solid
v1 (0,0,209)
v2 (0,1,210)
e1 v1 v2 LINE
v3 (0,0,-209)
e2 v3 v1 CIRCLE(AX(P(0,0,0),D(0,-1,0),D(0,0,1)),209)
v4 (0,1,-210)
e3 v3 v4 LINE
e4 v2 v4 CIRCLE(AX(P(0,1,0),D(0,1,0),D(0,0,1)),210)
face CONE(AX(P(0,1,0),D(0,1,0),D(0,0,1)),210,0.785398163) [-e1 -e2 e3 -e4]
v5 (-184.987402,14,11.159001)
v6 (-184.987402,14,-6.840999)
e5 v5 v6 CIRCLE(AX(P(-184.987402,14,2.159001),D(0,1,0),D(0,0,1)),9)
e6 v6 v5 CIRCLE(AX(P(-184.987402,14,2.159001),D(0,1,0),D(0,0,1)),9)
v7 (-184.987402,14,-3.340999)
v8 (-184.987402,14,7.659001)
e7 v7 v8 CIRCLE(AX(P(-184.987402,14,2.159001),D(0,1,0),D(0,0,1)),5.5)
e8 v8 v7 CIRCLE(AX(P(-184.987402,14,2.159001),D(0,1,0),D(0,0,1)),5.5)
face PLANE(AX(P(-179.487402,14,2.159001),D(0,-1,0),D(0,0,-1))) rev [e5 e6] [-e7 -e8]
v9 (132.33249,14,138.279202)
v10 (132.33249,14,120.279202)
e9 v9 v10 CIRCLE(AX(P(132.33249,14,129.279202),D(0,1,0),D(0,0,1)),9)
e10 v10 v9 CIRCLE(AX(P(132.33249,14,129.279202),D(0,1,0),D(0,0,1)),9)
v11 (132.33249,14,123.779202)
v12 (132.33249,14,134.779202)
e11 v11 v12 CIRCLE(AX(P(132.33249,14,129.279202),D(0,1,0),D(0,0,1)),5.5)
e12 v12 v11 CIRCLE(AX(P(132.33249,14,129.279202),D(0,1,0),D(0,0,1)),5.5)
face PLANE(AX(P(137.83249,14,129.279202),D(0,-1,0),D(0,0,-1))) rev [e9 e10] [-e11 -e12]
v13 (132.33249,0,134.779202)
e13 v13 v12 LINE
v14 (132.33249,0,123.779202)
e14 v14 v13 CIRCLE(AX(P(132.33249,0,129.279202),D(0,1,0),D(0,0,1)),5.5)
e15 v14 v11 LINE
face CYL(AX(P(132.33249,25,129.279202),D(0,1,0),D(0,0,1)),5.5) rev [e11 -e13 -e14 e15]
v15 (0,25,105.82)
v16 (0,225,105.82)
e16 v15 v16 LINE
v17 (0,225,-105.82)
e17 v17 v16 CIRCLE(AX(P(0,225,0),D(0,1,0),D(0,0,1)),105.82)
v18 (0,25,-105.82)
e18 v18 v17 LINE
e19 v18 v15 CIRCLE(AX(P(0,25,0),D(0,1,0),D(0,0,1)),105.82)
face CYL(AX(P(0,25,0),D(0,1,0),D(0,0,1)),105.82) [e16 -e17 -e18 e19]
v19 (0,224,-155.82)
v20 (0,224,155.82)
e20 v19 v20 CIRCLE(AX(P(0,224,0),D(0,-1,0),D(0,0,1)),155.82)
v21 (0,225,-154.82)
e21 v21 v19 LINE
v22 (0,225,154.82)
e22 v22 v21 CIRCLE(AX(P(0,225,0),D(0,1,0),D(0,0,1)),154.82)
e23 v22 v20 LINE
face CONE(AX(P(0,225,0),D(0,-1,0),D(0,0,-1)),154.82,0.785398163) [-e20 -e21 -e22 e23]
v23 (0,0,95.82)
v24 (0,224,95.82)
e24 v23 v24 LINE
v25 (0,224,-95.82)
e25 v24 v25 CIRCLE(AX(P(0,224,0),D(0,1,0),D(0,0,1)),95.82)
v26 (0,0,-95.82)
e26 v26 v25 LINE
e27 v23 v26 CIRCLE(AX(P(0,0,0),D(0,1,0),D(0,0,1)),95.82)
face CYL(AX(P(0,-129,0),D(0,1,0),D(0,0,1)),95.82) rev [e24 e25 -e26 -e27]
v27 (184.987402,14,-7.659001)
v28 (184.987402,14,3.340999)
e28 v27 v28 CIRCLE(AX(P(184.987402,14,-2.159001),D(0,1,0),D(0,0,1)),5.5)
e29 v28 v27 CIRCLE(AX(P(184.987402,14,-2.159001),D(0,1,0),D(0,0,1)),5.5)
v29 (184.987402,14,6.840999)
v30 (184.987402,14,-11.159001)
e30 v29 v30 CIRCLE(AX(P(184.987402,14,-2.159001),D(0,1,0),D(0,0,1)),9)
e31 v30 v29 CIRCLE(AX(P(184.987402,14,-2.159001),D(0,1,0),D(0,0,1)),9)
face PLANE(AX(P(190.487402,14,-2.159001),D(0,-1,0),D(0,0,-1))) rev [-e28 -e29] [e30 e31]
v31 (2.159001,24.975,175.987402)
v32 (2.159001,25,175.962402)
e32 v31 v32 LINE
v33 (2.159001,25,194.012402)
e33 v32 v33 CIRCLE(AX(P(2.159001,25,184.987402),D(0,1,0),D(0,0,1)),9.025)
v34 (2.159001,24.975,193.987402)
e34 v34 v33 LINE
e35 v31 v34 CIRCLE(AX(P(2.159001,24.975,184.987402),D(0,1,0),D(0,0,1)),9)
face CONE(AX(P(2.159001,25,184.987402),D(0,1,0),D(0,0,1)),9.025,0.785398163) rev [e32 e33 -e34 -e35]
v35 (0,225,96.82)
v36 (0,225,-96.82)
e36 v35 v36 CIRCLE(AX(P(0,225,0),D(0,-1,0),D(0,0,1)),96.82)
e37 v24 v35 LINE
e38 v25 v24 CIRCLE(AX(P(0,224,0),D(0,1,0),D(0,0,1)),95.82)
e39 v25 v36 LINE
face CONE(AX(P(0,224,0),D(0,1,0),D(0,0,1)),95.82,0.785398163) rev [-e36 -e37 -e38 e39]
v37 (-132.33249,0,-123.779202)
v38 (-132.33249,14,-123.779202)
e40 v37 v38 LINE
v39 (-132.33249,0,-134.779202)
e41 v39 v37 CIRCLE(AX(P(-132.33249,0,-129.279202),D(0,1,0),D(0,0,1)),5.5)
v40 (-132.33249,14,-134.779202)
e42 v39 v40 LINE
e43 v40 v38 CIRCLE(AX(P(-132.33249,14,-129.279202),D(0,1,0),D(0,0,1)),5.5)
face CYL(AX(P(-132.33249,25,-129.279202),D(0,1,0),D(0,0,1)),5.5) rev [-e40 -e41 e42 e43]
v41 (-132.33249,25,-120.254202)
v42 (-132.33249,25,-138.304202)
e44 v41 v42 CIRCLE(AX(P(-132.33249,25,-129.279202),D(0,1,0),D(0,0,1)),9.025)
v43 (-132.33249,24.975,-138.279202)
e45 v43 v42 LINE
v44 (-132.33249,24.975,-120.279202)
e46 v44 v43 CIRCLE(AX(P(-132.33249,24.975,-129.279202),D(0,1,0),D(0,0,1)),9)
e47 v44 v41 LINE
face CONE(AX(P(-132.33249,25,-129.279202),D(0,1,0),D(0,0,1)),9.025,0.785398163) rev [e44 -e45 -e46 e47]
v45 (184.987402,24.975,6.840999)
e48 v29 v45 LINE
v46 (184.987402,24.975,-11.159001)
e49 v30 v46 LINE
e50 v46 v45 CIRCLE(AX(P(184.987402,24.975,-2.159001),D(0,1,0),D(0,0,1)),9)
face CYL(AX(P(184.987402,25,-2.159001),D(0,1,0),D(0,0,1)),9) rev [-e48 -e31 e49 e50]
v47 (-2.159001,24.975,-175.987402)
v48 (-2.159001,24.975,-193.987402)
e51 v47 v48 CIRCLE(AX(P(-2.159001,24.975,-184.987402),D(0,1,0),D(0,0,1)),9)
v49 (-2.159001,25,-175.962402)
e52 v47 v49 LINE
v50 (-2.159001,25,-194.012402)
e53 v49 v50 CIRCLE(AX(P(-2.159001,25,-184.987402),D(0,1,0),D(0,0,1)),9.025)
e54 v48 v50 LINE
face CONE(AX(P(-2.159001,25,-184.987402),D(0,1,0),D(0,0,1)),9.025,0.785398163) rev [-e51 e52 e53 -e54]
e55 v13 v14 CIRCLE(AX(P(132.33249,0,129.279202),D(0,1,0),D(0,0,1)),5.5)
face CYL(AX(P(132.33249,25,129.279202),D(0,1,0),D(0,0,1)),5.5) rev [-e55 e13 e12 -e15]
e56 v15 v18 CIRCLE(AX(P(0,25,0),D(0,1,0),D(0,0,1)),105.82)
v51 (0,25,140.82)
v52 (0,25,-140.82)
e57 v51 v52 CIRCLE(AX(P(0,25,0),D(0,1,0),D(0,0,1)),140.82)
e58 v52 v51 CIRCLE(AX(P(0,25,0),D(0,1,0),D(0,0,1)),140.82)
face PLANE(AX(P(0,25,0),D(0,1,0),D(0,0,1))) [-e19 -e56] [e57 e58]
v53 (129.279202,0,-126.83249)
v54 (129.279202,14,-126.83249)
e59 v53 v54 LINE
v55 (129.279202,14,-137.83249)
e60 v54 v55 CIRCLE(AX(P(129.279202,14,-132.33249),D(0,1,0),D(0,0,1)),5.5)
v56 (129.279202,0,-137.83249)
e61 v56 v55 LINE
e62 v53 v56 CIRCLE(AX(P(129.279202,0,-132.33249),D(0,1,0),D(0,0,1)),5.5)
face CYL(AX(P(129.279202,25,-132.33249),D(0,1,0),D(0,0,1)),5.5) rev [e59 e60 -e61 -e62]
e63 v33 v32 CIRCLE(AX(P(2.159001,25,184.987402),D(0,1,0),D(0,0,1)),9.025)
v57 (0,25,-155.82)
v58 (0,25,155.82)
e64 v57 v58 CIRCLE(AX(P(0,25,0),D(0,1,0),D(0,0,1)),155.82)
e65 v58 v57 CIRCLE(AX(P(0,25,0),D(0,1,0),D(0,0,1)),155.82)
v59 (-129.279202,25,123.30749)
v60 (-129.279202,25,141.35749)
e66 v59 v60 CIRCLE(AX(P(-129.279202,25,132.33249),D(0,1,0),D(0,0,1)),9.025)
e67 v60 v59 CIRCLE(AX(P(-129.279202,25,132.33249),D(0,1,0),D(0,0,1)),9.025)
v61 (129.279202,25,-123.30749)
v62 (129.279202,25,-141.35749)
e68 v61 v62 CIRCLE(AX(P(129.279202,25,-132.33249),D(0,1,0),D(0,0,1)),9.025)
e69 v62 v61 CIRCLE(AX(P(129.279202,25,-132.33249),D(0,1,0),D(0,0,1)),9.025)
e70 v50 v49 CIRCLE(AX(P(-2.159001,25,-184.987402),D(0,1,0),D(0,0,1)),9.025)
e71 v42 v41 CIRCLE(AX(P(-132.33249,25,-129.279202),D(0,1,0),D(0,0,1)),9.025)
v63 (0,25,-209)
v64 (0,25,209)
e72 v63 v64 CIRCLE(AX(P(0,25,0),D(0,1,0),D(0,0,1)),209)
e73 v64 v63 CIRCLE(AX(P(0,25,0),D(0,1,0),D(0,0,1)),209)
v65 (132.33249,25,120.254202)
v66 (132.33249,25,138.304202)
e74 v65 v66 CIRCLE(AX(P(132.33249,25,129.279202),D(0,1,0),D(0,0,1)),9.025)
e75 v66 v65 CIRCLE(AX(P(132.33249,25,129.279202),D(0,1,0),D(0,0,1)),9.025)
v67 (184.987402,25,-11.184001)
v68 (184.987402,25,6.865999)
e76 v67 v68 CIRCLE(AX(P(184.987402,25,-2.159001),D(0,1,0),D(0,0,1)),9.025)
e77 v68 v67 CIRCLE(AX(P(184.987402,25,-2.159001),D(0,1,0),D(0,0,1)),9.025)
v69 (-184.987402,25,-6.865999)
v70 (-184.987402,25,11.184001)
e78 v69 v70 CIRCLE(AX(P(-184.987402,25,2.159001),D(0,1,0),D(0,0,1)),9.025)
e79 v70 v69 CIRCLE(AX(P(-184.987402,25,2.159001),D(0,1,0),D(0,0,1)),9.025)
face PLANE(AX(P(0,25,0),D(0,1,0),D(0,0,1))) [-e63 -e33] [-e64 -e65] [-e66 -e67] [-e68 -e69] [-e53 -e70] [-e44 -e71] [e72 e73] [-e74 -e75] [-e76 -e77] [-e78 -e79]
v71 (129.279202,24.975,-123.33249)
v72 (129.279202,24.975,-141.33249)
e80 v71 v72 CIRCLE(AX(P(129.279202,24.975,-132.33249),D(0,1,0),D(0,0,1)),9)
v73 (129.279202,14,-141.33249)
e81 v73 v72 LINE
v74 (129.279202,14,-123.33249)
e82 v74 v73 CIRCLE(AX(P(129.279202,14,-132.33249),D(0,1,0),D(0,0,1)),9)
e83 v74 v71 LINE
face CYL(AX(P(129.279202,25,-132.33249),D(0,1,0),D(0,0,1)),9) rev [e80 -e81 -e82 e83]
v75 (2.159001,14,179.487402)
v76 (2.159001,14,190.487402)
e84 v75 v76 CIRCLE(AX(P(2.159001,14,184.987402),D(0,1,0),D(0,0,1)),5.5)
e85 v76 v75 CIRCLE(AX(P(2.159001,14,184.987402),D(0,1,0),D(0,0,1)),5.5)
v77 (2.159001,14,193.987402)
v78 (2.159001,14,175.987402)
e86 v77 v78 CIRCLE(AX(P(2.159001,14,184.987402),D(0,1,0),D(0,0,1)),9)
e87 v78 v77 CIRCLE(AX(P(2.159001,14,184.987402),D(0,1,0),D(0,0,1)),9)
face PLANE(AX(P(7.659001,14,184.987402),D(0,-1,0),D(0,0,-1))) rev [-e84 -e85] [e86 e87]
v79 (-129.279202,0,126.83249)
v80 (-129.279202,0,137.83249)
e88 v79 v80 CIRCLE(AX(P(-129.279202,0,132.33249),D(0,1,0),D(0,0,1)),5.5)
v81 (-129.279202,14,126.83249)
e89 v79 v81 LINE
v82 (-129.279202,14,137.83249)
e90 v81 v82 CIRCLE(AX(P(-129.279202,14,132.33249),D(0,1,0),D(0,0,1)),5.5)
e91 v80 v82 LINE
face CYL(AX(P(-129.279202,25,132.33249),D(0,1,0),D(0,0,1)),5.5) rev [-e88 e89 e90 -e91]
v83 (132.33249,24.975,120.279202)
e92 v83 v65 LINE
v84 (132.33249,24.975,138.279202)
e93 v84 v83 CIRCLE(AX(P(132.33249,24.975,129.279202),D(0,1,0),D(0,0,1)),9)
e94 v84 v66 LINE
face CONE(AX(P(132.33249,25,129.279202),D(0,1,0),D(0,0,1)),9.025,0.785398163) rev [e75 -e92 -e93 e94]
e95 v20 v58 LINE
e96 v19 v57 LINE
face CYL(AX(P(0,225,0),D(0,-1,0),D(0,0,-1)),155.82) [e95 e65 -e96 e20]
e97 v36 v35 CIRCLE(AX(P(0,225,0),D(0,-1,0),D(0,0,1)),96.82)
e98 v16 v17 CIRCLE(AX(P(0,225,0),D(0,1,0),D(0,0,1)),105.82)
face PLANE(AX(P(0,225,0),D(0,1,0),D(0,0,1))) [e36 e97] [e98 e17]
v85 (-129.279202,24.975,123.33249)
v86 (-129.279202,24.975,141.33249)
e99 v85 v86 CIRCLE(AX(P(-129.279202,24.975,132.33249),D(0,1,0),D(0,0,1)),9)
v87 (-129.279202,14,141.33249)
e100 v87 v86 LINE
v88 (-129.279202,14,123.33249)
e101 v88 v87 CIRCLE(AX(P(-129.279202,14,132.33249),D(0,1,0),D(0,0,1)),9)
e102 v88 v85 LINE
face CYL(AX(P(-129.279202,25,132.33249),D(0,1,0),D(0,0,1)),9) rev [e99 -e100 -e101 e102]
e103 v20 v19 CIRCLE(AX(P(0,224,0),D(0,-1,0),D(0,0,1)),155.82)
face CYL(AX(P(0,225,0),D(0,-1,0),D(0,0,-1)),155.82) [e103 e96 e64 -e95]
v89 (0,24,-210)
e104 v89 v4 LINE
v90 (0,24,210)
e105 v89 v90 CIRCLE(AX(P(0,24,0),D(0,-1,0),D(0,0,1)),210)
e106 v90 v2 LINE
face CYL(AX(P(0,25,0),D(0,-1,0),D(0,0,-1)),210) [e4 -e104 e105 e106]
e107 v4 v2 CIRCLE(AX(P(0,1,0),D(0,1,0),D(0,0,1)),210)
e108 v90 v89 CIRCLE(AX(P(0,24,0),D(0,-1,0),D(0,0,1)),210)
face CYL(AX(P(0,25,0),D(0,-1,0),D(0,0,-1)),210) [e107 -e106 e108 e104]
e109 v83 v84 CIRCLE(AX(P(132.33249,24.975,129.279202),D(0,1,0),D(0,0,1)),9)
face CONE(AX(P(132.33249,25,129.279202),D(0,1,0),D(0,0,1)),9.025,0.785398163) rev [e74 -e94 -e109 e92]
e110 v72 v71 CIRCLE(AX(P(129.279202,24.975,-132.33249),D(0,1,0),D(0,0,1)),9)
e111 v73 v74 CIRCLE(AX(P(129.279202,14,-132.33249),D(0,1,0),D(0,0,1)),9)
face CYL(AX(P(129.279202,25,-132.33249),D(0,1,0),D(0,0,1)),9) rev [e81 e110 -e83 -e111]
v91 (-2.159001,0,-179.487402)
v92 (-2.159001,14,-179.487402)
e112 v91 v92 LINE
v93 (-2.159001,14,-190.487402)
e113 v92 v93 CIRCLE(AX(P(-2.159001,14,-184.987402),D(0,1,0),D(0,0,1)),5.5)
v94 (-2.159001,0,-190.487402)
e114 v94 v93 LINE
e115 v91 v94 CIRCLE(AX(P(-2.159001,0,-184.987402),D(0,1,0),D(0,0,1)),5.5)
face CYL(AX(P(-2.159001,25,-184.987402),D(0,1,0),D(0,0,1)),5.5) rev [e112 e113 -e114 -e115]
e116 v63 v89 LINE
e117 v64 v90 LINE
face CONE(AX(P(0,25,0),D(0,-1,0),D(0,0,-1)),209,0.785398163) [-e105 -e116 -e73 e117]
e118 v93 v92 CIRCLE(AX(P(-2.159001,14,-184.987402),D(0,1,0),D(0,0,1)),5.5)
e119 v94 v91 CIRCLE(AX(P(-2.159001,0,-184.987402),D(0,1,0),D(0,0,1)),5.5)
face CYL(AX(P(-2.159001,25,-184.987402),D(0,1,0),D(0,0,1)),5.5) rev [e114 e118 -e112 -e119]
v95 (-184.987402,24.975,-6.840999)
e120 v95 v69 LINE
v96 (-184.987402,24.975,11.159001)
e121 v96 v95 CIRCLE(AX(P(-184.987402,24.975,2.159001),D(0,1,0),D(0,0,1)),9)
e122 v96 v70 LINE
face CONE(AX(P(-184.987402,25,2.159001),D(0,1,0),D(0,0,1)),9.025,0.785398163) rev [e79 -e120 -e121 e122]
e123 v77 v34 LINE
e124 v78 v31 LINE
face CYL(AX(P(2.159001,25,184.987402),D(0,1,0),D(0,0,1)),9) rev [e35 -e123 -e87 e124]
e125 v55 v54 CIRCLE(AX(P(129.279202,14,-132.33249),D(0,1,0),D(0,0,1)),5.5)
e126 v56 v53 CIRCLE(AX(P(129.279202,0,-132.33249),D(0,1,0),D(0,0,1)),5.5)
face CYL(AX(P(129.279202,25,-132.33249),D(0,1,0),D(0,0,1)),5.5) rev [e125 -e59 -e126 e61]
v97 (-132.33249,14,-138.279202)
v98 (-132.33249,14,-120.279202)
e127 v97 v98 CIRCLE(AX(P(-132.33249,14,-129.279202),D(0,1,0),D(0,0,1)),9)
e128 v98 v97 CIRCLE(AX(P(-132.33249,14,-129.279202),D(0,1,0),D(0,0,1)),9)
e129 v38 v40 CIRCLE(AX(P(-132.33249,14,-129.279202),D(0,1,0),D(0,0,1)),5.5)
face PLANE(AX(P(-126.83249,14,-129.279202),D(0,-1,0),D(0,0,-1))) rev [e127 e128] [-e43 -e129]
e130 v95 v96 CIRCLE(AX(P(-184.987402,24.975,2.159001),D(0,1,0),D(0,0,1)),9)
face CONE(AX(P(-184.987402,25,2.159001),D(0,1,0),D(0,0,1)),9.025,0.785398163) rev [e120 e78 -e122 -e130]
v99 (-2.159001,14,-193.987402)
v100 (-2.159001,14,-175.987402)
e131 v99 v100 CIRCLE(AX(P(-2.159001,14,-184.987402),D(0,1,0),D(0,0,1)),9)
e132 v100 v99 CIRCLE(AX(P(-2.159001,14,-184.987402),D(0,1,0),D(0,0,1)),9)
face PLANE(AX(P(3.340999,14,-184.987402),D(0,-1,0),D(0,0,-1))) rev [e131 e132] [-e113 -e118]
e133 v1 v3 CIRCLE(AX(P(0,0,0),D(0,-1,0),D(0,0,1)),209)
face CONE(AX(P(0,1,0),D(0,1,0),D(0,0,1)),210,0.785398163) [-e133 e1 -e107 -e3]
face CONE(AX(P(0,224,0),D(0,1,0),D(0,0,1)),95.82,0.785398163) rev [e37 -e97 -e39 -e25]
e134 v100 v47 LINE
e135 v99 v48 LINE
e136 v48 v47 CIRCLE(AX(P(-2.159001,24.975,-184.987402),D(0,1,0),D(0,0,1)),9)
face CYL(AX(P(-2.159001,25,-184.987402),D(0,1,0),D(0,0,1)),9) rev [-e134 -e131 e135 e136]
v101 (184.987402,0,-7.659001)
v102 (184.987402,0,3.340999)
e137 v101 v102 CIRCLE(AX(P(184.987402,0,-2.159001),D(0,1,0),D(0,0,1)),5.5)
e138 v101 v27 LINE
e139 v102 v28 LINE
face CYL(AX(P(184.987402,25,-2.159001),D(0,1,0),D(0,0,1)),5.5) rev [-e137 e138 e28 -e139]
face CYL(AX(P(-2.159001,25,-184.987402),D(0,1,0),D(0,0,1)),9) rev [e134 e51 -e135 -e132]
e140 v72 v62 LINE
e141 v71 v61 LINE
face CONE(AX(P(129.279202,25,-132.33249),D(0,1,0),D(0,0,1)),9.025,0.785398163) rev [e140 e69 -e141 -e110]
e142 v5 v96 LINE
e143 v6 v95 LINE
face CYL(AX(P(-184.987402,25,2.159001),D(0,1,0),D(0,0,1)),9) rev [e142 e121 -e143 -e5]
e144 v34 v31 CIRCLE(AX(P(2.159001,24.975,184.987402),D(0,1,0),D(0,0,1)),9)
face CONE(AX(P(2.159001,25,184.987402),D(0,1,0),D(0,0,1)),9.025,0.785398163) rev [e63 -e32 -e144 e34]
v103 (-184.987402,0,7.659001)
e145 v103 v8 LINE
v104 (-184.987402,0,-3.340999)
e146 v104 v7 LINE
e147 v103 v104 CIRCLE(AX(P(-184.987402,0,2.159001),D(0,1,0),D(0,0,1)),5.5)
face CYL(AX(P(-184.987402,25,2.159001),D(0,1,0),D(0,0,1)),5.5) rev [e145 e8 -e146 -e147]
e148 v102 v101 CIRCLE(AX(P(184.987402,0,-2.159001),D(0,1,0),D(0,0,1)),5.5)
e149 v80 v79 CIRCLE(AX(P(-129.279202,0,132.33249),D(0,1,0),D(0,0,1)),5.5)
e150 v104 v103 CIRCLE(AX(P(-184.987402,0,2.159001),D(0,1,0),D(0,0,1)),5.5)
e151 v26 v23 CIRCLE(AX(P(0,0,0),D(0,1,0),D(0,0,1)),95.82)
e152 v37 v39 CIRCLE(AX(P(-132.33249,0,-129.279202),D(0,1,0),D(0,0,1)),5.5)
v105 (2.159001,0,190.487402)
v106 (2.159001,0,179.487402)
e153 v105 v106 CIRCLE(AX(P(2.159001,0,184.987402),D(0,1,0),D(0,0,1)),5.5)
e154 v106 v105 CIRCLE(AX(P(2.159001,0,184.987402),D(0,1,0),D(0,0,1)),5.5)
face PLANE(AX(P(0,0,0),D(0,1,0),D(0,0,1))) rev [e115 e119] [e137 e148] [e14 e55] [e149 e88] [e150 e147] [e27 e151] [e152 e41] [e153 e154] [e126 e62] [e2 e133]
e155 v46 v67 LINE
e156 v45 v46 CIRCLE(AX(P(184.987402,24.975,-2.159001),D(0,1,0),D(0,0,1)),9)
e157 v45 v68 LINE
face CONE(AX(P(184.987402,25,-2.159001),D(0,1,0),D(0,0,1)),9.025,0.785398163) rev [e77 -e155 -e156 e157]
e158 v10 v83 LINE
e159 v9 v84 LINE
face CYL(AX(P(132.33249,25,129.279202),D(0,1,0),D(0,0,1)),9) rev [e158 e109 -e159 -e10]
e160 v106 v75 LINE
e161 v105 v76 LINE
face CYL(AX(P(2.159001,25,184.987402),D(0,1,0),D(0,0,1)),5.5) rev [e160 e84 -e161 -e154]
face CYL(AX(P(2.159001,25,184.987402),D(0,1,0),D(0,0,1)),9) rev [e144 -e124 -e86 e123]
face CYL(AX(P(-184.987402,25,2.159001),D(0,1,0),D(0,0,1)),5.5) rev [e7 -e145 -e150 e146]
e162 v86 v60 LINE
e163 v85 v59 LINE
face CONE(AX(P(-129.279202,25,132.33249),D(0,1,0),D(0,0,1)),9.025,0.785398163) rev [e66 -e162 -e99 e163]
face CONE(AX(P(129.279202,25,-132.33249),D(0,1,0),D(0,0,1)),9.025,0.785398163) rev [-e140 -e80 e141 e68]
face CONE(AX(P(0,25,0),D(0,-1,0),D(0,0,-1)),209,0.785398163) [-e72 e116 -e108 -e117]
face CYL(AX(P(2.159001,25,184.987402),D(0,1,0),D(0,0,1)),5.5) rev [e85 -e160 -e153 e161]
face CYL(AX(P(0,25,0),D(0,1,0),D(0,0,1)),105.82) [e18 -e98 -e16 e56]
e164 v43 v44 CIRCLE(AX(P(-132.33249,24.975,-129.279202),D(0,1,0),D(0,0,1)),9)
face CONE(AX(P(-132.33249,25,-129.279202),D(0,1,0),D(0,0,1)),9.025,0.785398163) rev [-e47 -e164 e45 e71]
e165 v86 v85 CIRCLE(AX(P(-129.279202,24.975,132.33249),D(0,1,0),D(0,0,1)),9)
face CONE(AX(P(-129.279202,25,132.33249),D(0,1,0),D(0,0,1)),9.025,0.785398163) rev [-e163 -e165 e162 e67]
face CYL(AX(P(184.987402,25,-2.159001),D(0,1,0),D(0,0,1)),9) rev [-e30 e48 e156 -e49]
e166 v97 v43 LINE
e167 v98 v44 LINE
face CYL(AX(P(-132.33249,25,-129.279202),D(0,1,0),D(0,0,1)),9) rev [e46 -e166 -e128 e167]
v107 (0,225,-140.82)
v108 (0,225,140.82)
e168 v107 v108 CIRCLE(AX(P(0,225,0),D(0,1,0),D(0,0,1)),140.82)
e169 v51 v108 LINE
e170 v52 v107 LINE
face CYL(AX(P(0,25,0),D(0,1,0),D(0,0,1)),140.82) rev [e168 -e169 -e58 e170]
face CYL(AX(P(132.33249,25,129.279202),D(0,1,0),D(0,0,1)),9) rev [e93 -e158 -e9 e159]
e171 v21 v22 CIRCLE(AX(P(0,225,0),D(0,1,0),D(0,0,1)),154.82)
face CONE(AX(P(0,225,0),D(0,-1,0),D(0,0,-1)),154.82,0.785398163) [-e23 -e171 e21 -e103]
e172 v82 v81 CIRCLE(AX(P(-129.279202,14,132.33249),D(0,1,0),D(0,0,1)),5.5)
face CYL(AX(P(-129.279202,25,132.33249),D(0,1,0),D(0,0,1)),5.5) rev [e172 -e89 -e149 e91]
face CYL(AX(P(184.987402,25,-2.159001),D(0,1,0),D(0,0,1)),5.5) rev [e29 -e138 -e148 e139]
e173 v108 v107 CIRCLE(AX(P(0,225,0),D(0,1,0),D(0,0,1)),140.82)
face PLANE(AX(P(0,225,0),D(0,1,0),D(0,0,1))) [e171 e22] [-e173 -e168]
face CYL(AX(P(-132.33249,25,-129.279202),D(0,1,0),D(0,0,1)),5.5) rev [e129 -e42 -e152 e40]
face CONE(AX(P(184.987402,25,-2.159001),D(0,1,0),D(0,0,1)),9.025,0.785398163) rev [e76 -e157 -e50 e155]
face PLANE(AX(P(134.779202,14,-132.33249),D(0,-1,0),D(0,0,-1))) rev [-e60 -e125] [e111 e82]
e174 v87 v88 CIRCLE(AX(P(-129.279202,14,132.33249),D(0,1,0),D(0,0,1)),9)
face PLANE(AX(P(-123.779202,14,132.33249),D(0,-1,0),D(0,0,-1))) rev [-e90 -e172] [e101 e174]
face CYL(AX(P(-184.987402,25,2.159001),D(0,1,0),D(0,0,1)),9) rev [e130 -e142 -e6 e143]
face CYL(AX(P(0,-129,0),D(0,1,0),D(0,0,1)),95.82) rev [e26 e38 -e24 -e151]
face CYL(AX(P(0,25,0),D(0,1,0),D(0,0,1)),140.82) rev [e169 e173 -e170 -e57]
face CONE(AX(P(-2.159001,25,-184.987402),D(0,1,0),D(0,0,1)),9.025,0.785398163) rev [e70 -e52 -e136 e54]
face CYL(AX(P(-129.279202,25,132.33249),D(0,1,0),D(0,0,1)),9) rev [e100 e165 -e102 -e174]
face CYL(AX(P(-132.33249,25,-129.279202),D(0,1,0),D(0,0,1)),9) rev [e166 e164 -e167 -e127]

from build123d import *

# Parameters (mm, degrees)
SKETCH_1_R               = 210
EXTRUDE_1_DEPTH          = 25
SKETCH_2_R               = 95.82
CUT_EXTRUDE_1_DEPTH      = 154
EXTRUDE_START            = 200
SKETCH_3_R               = 155.82
SKETCH_3_R_2             = 95.82
EXTRUDE_2_DEPTH          = 200
CHAMFER_1_SIZE           = 1
SKETCH_7_R               = 140.82
SKETCH_7_R_2             = 105.82
CUT_EXTRUDE_3_DEPTH      = 200
PATTERN_CIRCULAR_2_COUNT = 8


with BuildPart() as part:
    # 草图1 → 凸台-拉伸1 (new body)
    with BuildSketch(Plane(origin=(0, 0, 0), x_dir=(1, 0, 0), z_dir=(0, 1, 0))):
        with Locations(Location((0, 0, 0), (0, 0, 270))):
            Circle(SKETCH_1_R)
    extrude(amount=EXTRUDE_1_DEPTH)

    # 草图2 → 切除-拉伸1 (cut)
    with BuildSketch(Plane(origin=(0, 25, 0), x_dir=(1, 0, 0), z_dir=(0, 1, 0))):
        with Locations(Location((0, 0, 0), (0, 0, 270))):
            Circle(SKETCH_2_R)
    extrude(amount=-CUT_EXTRUDE_1_DEPTH, mode=Mode.SUBTRACT)

    # 草图3 → 凸台-拉伸2 (add)
    with BuildSketch(Plane(origin=(0, 25, 0), x_dir=(1, 0, 0), z_dir=(0, 1, 0)).offset(EXTRUDE_START)):
        with Locations(Location((0, 0, 0), (0, 0, 270))):
            Circle(SKETCH_3_R)
        with Locations(Location((0, 0, 0), (0, 0, 270))):
            Circle(SKETCH_3_R_2, mode=Mode.SUBTRACT)
    extrude(amount=-EXTRUDE_2_DEPTH)

    # 倒角1
    chamfer_1_edges = [part.edges().sort_by_distance(p)[0] for p in [
        (0, 225, -155.82),
        (0, 225, -95.82),
        (0, 0, -210),
        (0, 25, -210),
    ]]
    chamfer(chamfer_1_edges, length=CHAMFER_1_SIZE)

    # 草图7 → 切除-拉伸3 (cut)
    with BuildSketch(Plane(origin=(0, 225, 0), x_dir=(1, 0, 0), z_dir=(0, 1, 0))):
        with Locations(Location((0, 0, 0), (0, 0, 270))):
            Circle(SKETCH_7_R)
        with Locations(Location((0, 0, 0), (0, 0, 270))):
            Circle(SKETCH_7_R_2, mode=Mode.SUBTRACT)
    extrude(amount=-CUT_EXTRUDE_3_DEPTH, mode=Mode.SUBTRACT)

    # 草图10 → M10 六角圆柱头螺钉的柱形沉头孔2 (revolve, cut)
    with BuildSketch(Plane(origin=(-184.987401502, 25, 2.159001035), x_dir=(0, 0, 1), z_dir=(1, 0, 0))):
        Polygon((0, 0), (0, 30.804733405), (5.5, 27.5), (5.5, 11), (9, 11), (9, 0.025), (9.025, 0), align=None)
    hole_wizard_m10_2 = revolve(axis=Axis((-184.987401502, 31.35, 2.159001035), (0, -1, 0)), mode=Mode.SUBTRACT)

    # 阵列(圆周)2: M10 六角圆柱头螺钉的柱形沉头孔2 ×8 about axis
    pattern_circular_2_axis = Axis((0, 0, 0), (0, 1, 0))
    for i in range(1, PATTERN_CIRCULAR_2_COUNT):
        add(hole_wizard_m10_2.rotate(pattern_circular_2_axis, i * 360 / PATTERN_CIRCULAR_2_COUNT), mode=Mode.SUBTRACT)


solid = part.part
